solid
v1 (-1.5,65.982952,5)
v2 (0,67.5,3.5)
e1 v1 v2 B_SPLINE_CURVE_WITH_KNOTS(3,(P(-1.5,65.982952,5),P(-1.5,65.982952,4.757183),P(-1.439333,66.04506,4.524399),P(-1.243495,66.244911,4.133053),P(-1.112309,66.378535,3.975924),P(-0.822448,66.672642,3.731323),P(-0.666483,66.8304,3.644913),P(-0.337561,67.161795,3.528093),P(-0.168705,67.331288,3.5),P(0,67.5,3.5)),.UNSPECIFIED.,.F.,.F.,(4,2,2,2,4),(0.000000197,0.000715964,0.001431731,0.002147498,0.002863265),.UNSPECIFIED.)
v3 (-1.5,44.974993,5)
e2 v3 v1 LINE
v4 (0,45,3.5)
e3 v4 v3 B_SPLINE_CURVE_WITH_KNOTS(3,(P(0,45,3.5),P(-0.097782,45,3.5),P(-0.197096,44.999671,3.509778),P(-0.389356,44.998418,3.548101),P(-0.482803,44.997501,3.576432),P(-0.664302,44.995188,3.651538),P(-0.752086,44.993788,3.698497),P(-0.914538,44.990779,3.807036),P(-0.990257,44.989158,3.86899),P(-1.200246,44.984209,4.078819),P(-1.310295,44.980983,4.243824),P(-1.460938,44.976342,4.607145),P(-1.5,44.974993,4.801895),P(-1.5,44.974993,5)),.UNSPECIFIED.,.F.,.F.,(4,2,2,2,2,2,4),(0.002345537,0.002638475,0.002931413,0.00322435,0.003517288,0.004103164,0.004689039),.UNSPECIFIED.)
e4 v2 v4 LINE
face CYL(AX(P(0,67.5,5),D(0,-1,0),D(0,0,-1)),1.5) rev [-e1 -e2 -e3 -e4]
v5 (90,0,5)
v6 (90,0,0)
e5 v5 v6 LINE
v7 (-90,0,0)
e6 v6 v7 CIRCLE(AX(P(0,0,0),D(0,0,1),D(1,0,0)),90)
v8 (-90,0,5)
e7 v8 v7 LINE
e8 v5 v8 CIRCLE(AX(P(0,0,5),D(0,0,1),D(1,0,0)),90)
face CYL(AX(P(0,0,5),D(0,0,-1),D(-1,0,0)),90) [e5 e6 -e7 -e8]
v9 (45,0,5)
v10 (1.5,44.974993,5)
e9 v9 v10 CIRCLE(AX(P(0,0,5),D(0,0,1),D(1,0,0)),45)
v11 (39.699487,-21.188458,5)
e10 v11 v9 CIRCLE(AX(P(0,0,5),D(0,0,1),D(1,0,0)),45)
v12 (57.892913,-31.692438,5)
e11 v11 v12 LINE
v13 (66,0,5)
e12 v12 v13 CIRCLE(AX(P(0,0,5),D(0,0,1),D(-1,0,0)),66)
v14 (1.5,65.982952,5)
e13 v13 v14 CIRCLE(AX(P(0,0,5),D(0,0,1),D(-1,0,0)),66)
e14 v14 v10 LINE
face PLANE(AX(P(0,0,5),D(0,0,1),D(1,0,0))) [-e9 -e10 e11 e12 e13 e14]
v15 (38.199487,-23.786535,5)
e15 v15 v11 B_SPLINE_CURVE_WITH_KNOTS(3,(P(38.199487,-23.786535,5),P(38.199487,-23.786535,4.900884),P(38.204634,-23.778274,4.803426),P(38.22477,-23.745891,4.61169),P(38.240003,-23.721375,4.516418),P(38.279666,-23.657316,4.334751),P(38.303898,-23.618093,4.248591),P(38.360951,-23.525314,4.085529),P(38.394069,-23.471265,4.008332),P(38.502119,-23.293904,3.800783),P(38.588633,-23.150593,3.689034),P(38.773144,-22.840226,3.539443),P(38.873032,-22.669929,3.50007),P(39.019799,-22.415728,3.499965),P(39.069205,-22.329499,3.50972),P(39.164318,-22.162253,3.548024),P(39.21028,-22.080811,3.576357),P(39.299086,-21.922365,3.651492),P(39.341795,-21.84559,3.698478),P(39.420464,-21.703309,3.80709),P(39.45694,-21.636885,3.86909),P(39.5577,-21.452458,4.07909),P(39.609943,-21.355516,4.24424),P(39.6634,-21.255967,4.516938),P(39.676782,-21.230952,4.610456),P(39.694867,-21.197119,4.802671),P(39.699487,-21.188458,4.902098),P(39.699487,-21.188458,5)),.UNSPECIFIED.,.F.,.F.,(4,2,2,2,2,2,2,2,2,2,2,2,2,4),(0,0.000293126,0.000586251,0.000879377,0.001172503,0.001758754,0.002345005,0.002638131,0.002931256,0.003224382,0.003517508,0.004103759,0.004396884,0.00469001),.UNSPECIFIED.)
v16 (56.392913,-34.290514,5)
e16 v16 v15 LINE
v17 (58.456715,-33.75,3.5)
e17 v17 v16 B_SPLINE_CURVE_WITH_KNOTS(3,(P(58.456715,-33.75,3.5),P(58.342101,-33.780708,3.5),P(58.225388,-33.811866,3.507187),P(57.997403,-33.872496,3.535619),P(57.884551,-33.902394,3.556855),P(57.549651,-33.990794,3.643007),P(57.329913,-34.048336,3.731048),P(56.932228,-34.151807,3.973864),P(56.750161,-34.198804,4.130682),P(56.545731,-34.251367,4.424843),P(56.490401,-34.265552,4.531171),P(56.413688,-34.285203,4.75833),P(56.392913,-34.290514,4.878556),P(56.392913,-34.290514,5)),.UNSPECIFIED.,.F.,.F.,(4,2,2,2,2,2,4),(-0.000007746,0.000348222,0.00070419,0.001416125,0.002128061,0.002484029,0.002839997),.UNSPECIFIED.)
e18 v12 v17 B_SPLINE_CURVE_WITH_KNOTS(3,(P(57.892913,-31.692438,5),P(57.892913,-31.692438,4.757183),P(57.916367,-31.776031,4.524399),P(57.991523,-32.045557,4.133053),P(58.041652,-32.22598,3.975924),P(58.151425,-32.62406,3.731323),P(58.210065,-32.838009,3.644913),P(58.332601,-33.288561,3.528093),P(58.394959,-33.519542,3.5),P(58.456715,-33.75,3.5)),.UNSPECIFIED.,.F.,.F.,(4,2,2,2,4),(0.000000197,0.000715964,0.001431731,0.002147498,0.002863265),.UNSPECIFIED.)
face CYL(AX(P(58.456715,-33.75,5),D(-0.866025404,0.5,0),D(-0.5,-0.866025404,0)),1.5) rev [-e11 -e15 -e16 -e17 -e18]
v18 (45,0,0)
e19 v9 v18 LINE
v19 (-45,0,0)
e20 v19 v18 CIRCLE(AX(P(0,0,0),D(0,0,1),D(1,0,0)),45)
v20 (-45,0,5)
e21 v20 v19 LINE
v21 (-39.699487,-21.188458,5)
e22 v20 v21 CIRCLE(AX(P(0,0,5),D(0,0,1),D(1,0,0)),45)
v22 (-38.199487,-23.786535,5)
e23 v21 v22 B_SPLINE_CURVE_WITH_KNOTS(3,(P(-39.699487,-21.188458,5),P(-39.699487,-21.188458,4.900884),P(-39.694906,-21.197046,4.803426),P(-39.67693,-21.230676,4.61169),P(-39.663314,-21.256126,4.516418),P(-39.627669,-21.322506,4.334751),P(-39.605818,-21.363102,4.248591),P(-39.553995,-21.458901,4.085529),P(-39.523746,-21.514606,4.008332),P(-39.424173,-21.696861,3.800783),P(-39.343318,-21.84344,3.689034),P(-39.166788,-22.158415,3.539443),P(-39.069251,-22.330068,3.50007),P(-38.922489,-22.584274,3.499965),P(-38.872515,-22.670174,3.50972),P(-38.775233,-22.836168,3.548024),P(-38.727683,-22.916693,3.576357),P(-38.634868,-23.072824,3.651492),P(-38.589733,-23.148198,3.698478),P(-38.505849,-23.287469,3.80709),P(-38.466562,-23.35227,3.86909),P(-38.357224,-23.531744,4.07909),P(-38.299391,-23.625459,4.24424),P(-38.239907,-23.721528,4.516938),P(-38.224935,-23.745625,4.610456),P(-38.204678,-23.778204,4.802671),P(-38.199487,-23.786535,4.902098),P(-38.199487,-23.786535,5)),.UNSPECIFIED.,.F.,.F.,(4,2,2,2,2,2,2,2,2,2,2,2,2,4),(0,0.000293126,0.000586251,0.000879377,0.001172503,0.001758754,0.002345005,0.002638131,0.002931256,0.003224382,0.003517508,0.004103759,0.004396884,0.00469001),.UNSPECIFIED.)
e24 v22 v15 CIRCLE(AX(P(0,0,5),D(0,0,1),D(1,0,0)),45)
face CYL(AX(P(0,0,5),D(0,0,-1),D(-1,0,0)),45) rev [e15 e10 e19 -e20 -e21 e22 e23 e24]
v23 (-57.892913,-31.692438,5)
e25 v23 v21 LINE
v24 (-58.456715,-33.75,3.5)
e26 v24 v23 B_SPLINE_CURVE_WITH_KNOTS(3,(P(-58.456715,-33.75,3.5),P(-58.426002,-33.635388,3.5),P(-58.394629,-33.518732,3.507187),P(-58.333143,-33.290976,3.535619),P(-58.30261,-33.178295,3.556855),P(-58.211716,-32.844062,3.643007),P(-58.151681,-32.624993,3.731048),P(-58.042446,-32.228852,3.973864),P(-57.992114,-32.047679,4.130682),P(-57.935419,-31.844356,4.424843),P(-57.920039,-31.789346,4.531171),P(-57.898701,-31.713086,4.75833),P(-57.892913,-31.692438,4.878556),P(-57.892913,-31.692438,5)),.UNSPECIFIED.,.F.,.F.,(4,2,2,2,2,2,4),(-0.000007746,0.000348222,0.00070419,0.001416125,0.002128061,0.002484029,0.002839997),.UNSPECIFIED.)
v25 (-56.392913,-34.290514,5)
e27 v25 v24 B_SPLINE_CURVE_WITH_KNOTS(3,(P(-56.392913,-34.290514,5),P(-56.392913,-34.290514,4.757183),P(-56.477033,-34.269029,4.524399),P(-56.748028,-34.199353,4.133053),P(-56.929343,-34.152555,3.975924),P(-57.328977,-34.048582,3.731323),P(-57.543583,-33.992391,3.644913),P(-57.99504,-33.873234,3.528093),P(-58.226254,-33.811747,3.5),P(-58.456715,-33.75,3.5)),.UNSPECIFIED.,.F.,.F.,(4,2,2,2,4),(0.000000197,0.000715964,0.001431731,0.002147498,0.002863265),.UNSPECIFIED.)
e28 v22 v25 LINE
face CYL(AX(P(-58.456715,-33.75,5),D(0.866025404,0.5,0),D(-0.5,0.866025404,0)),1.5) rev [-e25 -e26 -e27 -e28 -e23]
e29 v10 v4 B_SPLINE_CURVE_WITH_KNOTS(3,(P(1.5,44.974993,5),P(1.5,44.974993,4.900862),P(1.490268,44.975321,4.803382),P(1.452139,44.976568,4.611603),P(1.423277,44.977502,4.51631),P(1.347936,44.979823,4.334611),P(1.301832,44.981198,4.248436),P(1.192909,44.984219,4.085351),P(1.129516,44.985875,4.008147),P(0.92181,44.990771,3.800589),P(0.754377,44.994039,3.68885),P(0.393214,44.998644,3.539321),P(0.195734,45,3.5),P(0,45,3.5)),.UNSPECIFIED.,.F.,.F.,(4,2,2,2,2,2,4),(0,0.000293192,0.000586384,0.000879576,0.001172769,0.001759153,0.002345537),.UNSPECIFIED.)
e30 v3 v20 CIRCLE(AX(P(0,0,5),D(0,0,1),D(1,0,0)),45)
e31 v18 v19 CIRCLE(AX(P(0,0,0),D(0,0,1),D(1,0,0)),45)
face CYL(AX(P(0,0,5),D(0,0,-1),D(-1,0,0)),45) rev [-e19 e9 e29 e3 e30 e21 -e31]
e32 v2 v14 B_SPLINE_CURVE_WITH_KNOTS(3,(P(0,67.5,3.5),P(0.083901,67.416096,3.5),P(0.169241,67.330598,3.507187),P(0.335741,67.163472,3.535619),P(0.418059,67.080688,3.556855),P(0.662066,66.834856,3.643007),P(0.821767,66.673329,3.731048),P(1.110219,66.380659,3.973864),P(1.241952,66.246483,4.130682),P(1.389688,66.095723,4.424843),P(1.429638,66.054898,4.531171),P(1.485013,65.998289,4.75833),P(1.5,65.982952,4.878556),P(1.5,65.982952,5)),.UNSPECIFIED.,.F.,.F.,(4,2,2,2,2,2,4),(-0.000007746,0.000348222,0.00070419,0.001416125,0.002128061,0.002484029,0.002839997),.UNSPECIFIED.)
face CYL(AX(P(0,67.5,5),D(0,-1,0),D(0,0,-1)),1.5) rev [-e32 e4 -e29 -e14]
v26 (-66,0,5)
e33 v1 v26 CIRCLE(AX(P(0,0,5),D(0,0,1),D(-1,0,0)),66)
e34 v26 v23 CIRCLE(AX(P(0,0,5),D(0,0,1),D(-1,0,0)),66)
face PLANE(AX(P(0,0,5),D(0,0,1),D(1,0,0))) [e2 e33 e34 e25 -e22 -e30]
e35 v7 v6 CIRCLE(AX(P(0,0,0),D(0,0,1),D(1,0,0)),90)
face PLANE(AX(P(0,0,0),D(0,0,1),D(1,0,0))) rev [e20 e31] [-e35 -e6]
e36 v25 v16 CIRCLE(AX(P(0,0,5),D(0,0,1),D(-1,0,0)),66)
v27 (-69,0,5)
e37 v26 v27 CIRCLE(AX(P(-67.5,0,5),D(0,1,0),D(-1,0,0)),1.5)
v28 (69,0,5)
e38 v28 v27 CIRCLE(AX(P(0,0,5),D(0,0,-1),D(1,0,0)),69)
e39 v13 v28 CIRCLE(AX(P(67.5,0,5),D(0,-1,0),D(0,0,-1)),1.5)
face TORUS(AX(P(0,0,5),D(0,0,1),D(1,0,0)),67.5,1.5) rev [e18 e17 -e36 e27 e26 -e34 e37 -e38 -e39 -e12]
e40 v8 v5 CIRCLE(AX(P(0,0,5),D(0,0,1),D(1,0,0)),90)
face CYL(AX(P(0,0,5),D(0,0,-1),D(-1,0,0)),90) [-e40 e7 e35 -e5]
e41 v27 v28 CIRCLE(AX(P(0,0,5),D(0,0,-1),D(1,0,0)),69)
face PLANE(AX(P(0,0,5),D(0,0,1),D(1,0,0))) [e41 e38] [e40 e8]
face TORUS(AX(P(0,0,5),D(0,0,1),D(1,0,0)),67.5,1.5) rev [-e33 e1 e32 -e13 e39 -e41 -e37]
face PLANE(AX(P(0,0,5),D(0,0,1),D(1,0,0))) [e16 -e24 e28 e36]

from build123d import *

# Parameters (mm, degrees)
SKETCH_1_R               = 90
SKETCH_1_R_2             = 45
EXTRUDE_1_DEPTH          = 5
SKETCH_3_R               = 1.5
SKETCH_5_R               = 1.5
CUT_EXTRUDE_2_DEPTH      = 67.5
PATTERN_CIRCULAR_1_COUNT = 3


with BuildPart() as part:
    # 草图1 → 凸台-拉伸1 (new body)
    with BuildSketch(Plane.XY):
        Circle(SKETCH_1_R)
        Circle(SKETCH_1_R_2, mode=Mode.SUBTRACT)
    extrude(amount=EXTRUDE_1_DEPTH)

    # 切除-扫描1: sweep along a path in 草图2
    with BuildLine(Plane.XY.offset(5)) as sweep_1_path:
        CenterArc((0, 0), 67.5, 0, 360)
    # 草图3 → 切除-扫描1 (sweep, cut)
    with BuildSketch(Plane(origin=(0, 0, 0), x_dir=(0, 0, -1), z_dir=(1, 0, 0))):
        with Locations((-5, 67.5)):
            Circle(SKETCH_3_R)
    sweep(path=sweep_1_path.line, mode=Mode.SUBTRACT)

    # 草图5 → 切除-拉伸2 (cut)
    with BuildSketch(Plane(origin=(0, 0, 0), x_dir=(1, 0, 0), z_dir=(0, 1, 0))):
        with Locations((0, -5)):
            Circle(SKETCH_5_R)
    cut_extrude_2 = extrude(amount=CUT_EXTRUDE_2_DEPTH, mode=Mode.SUBTRACT)

    # 阵列(圆周)1: 切除-拉伸2 ×3 about axis
    pattern_circular_1_axis = Axis((0, 0, 5), (0, 0, -1))
    for i in range(1, PATTERN_CIRCULAR_1_COUNT):
        add(cut_extrude_2.rotate(pattern_circular_1_axis, i * 360 / PATTERN_CIRCULAR_1_COUNT), mode=Mode.SUBTRACT)


solid = part.part
